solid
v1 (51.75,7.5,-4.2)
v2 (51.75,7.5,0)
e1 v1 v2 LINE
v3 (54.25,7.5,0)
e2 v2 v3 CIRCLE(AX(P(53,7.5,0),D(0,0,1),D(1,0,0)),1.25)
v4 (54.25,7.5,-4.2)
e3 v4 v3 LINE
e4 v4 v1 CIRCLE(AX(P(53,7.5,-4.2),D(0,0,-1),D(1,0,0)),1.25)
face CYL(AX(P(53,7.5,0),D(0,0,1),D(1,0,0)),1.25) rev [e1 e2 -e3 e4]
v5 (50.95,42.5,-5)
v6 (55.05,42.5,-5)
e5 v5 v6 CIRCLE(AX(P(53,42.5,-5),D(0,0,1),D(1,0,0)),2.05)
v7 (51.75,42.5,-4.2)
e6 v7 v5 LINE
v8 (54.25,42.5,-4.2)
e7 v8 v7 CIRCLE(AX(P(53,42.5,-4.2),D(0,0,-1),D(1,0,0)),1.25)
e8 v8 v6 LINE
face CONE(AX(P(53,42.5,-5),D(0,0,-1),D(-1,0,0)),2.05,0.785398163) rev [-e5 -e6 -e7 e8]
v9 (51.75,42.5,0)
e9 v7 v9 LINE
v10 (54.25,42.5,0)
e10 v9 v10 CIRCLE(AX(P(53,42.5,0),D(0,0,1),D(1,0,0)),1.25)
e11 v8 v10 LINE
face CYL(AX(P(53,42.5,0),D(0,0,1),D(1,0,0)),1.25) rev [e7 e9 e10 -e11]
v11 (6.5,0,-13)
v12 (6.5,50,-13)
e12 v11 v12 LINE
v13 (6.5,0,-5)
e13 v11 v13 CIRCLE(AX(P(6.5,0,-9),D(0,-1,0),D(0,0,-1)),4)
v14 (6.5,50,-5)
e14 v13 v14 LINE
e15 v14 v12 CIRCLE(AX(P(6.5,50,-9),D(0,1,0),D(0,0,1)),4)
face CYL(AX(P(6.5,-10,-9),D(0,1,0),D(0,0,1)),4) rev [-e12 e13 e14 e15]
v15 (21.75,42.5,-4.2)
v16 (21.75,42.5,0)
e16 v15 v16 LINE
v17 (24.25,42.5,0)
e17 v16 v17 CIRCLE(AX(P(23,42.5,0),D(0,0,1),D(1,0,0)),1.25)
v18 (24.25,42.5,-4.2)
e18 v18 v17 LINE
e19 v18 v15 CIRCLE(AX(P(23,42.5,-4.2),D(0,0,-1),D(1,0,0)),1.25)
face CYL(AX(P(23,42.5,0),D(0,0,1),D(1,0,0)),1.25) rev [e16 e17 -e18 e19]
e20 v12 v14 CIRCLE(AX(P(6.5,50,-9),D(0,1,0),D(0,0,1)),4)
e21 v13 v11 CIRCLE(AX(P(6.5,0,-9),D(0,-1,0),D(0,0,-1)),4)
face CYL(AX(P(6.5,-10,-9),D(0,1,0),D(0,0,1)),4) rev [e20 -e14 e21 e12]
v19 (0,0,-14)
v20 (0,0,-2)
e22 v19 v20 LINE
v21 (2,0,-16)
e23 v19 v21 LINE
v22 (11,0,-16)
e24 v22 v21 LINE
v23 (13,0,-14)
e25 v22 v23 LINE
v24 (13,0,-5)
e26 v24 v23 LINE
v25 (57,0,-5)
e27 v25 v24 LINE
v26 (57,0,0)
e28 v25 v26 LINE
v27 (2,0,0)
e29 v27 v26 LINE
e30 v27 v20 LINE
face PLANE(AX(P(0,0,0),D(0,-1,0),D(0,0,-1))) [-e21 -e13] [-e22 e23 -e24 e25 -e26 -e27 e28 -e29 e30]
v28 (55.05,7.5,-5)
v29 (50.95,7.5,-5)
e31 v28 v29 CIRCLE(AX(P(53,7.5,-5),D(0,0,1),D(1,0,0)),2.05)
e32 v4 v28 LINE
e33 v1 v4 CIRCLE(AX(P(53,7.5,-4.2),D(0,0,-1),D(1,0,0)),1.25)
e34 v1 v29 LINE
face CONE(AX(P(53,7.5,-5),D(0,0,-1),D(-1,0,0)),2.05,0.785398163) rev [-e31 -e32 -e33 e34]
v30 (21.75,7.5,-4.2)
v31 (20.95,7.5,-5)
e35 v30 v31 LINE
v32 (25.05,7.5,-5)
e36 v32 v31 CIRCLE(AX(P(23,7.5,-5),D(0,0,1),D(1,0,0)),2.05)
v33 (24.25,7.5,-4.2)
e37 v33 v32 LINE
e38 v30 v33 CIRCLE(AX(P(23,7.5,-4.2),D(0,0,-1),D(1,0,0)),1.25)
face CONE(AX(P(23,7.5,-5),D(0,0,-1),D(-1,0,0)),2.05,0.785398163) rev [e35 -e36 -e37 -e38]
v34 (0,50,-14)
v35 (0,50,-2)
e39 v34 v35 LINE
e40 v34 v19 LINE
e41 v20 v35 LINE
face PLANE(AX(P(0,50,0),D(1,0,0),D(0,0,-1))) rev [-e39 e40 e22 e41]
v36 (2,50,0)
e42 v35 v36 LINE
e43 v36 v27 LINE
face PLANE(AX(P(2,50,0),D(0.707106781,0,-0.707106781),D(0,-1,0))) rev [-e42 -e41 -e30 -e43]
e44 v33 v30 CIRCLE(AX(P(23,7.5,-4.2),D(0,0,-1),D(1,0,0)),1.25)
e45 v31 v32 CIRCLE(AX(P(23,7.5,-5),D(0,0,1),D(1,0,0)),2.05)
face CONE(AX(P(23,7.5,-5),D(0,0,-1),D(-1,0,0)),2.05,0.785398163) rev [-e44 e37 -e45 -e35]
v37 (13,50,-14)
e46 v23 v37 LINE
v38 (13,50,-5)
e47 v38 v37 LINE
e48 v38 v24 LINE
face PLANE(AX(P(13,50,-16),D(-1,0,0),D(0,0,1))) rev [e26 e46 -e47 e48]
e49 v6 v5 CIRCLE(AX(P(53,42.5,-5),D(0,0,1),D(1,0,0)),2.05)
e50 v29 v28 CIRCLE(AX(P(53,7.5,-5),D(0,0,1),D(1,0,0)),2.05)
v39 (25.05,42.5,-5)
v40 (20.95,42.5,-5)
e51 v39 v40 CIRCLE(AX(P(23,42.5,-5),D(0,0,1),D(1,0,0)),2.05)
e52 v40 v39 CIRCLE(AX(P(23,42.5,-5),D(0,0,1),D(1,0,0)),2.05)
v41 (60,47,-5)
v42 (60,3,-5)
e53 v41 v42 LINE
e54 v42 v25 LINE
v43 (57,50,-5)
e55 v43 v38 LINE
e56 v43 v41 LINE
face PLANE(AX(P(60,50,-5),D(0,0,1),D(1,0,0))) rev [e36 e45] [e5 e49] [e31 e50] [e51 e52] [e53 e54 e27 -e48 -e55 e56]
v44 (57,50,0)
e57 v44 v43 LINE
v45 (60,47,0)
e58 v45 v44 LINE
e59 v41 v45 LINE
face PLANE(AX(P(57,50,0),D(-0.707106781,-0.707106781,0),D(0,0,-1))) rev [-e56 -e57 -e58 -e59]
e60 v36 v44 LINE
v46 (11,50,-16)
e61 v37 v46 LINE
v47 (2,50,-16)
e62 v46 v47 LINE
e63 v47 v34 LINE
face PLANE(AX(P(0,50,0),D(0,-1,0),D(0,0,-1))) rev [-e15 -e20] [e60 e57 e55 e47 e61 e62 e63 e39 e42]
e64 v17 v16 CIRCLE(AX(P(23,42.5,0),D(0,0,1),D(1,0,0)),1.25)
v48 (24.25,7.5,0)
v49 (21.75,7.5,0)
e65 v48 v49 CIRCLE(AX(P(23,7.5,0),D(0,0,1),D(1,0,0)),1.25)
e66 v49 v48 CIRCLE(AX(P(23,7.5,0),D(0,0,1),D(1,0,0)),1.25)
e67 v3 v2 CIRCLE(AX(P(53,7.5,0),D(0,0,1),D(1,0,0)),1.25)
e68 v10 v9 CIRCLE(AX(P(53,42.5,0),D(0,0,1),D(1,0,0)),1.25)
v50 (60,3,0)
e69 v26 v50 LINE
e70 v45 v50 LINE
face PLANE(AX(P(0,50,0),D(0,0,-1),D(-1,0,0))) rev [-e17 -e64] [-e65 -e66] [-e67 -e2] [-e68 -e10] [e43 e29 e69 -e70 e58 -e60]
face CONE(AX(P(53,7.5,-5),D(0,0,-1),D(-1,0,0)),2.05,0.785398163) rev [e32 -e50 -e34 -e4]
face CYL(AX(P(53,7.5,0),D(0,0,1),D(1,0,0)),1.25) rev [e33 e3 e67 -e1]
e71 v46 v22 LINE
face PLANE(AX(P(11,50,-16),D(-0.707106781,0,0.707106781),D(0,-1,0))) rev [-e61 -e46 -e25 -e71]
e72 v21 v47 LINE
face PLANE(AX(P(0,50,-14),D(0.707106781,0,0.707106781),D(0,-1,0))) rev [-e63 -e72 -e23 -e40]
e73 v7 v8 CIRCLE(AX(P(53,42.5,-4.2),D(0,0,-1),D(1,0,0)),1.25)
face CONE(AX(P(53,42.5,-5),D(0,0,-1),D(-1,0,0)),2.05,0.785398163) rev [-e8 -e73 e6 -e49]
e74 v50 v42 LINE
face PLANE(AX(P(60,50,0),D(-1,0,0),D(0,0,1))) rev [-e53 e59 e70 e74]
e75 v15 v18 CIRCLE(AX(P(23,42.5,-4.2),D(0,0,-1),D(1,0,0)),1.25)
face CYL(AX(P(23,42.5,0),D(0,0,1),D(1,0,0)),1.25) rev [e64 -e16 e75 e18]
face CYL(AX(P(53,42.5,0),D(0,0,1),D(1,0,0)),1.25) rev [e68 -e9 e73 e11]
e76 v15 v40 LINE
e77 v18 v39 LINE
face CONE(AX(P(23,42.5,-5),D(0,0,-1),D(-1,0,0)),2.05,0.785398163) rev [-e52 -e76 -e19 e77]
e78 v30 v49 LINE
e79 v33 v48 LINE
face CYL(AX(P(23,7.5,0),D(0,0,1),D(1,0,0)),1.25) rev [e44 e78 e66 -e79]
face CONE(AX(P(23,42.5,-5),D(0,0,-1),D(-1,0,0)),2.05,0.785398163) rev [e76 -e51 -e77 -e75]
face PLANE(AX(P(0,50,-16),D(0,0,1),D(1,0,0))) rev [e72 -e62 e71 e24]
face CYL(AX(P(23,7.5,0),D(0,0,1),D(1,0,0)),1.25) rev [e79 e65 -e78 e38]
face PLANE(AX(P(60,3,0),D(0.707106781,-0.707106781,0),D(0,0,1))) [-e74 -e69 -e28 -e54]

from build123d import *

# Parameters (mm, degrees)
BOSS_EXTRUDE1_DEPTH   = 50
SKETCH2_R             = 0.75
CUT_EXTRUDE1_DEPTH    = 10
SKETCH3_R             = 4
CUT_EXTRUDE2_DEPTH    = 60
CHAMFER1_SIZE         = 2
LPATTERN1_COUNT       = 2
LPATTERN1_PITCH       = 30
CHAMFER2_SIZE         = 3
M3_TAPPED_HOLE1_D     = 2.5
M3_TAPPED_HOLE1_DEPTH = 7.5
M3_TAPPED_HOLE1_TIP   = 0.751075774
CHAMFER3_SIZE         = 0.8


with BuildPart() as part:
    # Sketch1 → Boss-Extrude1 (new body)
    with BuildSketch(Plane(origin=(0, 0, 0), x_dir=(1, 0, 0), z_dir=(0, 1, 0))):
        Polygon((0, 0), (60, 0), (60, 5), (13, 5), (13, 16), (0, 16), align=None)
    extrude(amount=BOSS_EXTRUDE1_DEPTH)

    # Sketch2 → Cut-Extrude1 (cut)
    with BuildSketch(Plane.XY):
        with Locations((53, 42.5)):
            Circle(SKETCH2_R)
        with Locations((53, 7.5)):
            Circle(SKETCH2_R)
    cut_extrude1 = extrude(amount=-CUT_EXTRUDE1_DEPTH, mode=Mode.SUBTRACT)

    # Sketch3 → Cut-Extrude2 (cut)
    with BuildSketch(Plane(origin=(0, 50, 0), x_dir=(1, 0, 0), z_dir=(0, 1, 0))):
        with Locations(Location((6.5, 9, 0), (0, 0, 270))):
            Circle(SKETCH3_R)
    extrude(amount=-CUT_EXTRUDE2_DEPTH, mode=Mode.SUBTRACT)

    # Chamfer1
    chamfer1_edges = [part.edges().sort_by_distance(p)[0] for p in [
        (0, 25, -16),
        (13, 25, -16),
        (0, 25, 0),
    ]]
    chamfer(chamfer1_edges, length=CHAMFER1_SIZE)

    # LPattern1: Cut-Extrude1 ×2
    with Locations(*[(-i * LPATTERN1_PITCH, 0, 0) for i in range(1, LPATTERN1_COUNT)]):
        add(cut_extrude1, mode=Mode.SUBTRACT)

    # Chamfer2
    chamfer2_edges = [part.edges().sort_by_distance(p)[0] for p in [
        (60, 50, -2.5),
        (60, 0, -2.5),
    ]]
    chamfer(chamfer2_edges, length=CHAMFER2_SIZE)

    # M3 Tapped Hole1
    with Locations(Plane(origin=(23, 42.5, 0), x_dir=(1, 0, 0), z_dir=(0, 0, 1))):
        with Locations((0, 0), (30, 0), (30, -35), (0, -35)):
            Hole(M3_TAPPED_HOLE1_D / 2, depth=M3_TAPPED_HOLE1_DEPTH)
            with Locations((0, 0, -(M3_TAPPED_HOLE1_DEPTH + M3_TAPPED_HOLE1_TIP / 2))):  # 118° drill point
                Cone(0, M3_TAPPED_HOLE1_D / 2, M3_TAPPED_HOLE1_TIP, mode=Mode.SUBTRACT)

    # Chamfer3
    chamfer3_edges = [part.edges().sort_by_distance(p)[0] for p in [
        (24.25, 7.5, -5),
        (54.25, 7.5, -5),
        (54.25, 42.5, -5),
        (24.25, 42.5, -5),
    ]]
    chamfer(chamfer3_edges, length=CHAMFER3_SIZE)


solid = part.part
